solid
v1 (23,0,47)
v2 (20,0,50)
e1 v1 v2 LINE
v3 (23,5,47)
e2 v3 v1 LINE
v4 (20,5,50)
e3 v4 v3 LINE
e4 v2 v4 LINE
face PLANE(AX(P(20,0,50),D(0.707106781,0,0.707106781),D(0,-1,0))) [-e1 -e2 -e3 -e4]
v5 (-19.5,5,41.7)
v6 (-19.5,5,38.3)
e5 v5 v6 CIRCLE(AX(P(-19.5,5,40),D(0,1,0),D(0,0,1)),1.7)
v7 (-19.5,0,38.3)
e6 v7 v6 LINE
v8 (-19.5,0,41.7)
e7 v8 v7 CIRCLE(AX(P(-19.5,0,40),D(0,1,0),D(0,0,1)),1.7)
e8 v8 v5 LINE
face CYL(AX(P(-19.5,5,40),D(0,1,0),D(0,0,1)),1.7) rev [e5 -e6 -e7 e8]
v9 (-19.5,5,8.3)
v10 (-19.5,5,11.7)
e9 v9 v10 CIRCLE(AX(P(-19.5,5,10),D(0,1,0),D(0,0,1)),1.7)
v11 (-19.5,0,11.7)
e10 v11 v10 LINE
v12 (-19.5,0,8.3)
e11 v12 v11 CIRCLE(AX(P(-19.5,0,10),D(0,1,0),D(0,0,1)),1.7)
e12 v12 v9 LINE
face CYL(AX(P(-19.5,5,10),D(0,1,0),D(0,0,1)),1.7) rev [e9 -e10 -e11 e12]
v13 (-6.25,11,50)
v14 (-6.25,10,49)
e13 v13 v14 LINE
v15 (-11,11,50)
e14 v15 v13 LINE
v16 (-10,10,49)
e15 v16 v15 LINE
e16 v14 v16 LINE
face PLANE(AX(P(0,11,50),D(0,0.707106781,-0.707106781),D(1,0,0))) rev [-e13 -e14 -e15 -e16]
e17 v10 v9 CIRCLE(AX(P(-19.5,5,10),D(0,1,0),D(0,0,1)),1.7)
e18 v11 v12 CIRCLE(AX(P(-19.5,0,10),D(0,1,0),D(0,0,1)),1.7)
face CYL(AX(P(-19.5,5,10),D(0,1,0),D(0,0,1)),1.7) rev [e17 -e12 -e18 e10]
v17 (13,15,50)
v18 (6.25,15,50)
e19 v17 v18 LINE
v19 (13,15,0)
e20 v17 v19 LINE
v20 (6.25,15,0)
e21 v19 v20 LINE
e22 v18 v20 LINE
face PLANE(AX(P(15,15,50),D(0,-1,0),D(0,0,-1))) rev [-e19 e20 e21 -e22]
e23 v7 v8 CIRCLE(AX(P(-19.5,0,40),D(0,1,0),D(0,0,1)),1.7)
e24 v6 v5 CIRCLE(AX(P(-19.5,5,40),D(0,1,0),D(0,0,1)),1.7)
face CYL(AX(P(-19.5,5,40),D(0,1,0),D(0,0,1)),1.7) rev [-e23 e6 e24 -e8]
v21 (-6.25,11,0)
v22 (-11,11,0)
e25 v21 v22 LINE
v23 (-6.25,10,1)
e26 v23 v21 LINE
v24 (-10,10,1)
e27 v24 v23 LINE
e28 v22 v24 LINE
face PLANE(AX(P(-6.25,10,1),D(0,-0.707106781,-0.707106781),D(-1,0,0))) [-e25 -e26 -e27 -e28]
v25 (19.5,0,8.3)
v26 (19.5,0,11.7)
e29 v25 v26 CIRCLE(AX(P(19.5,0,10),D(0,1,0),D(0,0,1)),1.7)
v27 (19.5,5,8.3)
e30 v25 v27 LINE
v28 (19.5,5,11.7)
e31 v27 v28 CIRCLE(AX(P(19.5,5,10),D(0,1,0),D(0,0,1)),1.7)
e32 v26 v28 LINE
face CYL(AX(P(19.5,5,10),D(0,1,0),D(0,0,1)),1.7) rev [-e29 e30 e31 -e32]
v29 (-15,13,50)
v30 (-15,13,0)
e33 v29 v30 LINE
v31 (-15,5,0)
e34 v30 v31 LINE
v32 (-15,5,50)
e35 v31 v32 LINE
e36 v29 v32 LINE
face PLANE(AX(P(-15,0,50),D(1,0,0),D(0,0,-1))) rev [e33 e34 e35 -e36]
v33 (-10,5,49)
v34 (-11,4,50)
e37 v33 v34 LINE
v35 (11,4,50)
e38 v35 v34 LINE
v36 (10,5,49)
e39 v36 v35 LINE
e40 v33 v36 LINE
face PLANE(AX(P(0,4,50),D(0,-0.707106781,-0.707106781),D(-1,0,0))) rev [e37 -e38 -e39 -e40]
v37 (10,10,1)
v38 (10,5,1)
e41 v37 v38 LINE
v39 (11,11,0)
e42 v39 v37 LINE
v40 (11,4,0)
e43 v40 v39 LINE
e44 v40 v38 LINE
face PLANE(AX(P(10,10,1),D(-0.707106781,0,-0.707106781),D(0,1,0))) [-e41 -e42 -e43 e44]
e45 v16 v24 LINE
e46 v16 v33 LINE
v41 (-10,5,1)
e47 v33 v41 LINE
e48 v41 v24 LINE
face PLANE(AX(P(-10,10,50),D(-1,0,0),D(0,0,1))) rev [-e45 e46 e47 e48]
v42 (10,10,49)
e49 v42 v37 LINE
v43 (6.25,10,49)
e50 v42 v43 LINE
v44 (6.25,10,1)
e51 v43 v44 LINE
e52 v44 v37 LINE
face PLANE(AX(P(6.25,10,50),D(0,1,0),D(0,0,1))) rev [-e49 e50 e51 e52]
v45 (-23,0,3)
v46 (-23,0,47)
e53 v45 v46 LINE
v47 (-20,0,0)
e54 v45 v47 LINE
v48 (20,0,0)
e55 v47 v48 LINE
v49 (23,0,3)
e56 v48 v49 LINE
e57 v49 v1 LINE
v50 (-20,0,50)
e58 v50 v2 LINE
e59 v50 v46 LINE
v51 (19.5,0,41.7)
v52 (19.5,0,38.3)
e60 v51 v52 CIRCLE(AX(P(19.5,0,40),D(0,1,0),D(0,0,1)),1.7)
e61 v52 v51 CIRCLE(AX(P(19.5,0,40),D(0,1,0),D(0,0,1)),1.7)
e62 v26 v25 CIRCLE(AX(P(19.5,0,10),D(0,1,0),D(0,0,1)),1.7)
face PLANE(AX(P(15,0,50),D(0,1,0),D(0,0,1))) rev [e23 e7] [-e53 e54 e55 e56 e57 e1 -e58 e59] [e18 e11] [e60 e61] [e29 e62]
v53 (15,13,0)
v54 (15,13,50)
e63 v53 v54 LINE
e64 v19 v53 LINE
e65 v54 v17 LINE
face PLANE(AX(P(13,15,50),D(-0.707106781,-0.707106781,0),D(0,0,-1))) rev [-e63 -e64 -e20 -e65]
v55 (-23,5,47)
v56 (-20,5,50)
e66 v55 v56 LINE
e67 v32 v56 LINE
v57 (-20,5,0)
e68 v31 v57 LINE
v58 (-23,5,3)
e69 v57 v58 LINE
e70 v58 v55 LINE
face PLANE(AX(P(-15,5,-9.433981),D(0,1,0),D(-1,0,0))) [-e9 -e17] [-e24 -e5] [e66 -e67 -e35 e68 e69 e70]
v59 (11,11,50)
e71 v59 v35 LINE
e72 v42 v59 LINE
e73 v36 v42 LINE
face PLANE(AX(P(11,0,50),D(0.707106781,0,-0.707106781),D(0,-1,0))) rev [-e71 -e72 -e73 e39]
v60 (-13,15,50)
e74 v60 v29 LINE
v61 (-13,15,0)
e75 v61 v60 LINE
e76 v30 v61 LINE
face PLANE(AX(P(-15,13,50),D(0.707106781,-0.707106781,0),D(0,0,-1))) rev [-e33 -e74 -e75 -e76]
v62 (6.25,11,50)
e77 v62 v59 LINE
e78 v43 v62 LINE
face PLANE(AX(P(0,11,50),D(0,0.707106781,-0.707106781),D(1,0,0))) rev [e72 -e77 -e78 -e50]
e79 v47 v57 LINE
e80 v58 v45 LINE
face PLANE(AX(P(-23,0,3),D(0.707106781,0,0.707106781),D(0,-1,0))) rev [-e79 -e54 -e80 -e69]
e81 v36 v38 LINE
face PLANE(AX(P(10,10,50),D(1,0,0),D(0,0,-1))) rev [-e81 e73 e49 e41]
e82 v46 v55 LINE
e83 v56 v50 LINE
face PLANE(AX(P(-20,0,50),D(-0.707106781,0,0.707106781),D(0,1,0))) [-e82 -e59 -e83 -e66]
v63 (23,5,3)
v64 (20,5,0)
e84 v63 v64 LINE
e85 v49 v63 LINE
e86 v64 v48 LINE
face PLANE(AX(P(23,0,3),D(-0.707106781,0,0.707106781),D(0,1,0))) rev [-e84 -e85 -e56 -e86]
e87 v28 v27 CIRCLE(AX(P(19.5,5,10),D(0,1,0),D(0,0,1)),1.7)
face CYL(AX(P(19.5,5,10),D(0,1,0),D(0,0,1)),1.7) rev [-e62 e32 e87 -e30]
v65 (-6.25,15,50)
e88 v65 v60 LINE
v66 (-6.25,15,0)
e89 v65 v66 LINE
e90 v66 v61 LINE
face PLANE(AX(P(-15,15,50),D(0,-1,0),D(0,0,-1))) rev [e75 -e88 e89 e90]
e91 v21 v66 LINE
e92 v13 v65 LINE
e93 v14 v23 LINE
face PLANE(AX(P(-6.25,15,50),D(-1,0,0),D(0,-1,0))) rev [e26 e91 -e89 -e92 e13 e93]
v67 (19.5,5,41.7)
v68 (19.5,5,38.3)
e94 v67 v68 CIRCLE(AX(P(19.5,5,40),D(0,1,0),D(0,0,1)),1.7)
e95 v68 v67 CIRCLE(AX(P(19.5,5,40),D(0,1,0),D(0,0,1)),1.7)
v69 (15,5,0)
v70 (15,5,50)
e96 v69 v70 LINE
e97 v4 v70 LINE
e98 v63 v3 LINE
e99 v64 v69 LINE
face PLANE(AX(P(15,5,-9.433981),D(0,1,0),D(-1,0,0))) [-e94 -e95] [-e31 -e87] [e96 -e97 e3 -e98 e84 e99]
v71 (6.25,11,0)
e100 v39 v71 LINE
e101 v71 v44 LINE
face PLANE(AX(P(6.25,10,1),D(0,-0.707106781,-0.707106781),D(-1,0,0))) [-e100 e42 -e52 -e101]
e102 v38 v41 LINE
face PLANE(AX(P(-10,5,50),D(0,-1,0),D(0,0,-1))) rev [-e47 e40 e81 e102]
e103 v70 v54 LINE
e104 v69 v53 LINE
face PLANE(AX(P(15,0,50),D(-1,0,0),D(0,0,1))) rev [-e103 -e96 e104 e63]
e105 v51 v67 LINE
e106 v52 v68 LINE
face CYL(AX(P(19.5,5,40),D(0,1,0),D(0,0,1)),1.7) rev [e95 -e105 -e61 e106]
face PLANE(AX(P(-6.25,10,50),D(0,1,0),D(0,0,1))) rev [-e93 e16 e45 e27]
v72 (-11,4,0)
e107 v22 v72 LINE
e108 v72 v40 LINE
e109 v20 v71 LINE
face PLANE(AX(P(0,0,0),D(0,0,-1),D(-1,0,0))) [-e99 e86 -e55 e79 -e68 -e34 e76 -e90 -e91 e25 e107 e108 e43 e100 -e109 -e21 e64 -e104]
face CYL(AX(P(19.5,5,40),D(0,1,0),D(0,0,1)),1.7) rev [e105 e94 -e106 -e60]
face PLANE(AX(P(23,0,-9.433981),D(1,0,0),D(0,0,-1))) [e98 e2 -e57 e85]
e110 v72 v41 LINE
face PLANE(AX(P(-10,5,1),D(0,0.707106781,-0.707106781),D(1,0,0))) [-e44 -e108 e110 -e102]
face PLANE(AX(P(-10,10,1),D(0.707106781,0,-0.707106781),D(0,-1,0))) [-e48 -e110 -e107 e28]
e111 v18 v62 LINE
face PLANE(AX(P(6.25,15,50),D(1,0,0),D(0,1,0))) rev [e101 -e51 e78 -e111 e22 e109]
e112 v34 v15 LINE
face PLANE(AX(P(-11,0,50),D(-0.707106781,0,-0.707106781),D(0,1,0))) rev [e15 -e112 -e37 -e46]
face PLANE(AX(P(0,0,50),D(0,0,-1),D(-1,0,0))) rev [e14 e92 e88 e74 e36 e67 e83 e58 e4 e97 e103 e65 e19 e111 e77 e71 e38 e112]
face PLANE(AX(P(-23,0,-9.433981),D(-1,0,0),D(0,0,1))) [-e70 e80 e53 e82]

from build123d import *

# Parameters (mm, degrees)
EXTRUDE_1_DEPTH    = 50
SKETCH_3_W         = 8
SKETCH_3_H         = 5
EXTRUDE_2_DEPTH    = 50
CHAMFER_1_SIZE     = 1
CHAMFER_2_SIZE     = 1
CHAMFER_3_SIZE     = 3
HOLE_WIZARD_M3_1_D = 3.4
CHAMFER_4_SIZE     = 2


with BuildPart() as part:
    # 草图1 → 凸台-拉伸1 (new body)
    with BuildSketch(Plane.XY):
        Polygon((15, 0), (-15, 0), (-15, 15), (-6.25, 15), (-6.25, 10), (-10, 10), (-10, 5), (10, 5), (10, 10), (6.25, 10), (6.25, 15), (15, 15), align=None)
    extrude(amount=EXTRUDE_1_DEPTH)

    # 草图3 → 凸台-拉伸2 (add)
    with BuildSketch(Plane.XY.offset(50)):
        with Locations((-19, 2.5)):
            Rectangle(SKETCH_3_W, SKETCH_3_H)
        with Locations((19, 2.5)):
            Rectangle(SKETCH_3_W, SKETCH_3_H)
    extrude(amount=-EXTRUDE_2_DEPTH)

    # 倒角1
    chamfer_1_edges = [part.edges().sort_by_distance(p)[0] for p in [
        (8.125, 10, 50),
        (10, 7.5, 50),
        (0, 5, 50),
        (-10, 7.5, 50),
        (-8.125, 10, 50),
    ]]
    chamfer(chamfer_1_edges, length=CHAMFER_1_SIZE)

    # 倒角2
    chamfer_2_edges = [part.edges().sort_by_distance(p)[0] for p in [
        (-8.125, 10, 0),
        (-10, 7.5, 0),
        (0, 5, 0),
        (10, 7.5, 0),
        (8.125, 10, 0),
    ]]
    chamfer(chamfer_2_edges, length=CHAMFER_2_SIZE)

    # 倒角3
    chamfer_3_edges = [part.edges().sort_by_distance(p)[0] for p in [
        (-23, 2.5, 50),
        (-23, 2.5, 0),
        (23, 2.5, 50),
        (23, 2.5, 0),
    ]]
    chamfer(chamfer_3_edges, length=CHAMFER_3_SIZE)

    # M3 间隙孔1 (through all)
    with Locations(Plane(origin=(0, 5, 0), x_dir=(1, 0, 0), z_dir=(0, 1, 0))):
        with Locations((-19.5, -10), (-19.5, -40), (19.5, -40), (19.5, -10)):
            Hole(HOLE_WIZARD_M3_1_D / 2)

    # 倒角4
    chamfer_4_edges = [part.edges().sort_by_distance(p)[0] for p in [
        (-15, 15, 25),
        (15, 15, 25),
    ]]
    chamfer(chamfer_4_edges, length=CHAMFER_4_SIZE)


solid = part.part
